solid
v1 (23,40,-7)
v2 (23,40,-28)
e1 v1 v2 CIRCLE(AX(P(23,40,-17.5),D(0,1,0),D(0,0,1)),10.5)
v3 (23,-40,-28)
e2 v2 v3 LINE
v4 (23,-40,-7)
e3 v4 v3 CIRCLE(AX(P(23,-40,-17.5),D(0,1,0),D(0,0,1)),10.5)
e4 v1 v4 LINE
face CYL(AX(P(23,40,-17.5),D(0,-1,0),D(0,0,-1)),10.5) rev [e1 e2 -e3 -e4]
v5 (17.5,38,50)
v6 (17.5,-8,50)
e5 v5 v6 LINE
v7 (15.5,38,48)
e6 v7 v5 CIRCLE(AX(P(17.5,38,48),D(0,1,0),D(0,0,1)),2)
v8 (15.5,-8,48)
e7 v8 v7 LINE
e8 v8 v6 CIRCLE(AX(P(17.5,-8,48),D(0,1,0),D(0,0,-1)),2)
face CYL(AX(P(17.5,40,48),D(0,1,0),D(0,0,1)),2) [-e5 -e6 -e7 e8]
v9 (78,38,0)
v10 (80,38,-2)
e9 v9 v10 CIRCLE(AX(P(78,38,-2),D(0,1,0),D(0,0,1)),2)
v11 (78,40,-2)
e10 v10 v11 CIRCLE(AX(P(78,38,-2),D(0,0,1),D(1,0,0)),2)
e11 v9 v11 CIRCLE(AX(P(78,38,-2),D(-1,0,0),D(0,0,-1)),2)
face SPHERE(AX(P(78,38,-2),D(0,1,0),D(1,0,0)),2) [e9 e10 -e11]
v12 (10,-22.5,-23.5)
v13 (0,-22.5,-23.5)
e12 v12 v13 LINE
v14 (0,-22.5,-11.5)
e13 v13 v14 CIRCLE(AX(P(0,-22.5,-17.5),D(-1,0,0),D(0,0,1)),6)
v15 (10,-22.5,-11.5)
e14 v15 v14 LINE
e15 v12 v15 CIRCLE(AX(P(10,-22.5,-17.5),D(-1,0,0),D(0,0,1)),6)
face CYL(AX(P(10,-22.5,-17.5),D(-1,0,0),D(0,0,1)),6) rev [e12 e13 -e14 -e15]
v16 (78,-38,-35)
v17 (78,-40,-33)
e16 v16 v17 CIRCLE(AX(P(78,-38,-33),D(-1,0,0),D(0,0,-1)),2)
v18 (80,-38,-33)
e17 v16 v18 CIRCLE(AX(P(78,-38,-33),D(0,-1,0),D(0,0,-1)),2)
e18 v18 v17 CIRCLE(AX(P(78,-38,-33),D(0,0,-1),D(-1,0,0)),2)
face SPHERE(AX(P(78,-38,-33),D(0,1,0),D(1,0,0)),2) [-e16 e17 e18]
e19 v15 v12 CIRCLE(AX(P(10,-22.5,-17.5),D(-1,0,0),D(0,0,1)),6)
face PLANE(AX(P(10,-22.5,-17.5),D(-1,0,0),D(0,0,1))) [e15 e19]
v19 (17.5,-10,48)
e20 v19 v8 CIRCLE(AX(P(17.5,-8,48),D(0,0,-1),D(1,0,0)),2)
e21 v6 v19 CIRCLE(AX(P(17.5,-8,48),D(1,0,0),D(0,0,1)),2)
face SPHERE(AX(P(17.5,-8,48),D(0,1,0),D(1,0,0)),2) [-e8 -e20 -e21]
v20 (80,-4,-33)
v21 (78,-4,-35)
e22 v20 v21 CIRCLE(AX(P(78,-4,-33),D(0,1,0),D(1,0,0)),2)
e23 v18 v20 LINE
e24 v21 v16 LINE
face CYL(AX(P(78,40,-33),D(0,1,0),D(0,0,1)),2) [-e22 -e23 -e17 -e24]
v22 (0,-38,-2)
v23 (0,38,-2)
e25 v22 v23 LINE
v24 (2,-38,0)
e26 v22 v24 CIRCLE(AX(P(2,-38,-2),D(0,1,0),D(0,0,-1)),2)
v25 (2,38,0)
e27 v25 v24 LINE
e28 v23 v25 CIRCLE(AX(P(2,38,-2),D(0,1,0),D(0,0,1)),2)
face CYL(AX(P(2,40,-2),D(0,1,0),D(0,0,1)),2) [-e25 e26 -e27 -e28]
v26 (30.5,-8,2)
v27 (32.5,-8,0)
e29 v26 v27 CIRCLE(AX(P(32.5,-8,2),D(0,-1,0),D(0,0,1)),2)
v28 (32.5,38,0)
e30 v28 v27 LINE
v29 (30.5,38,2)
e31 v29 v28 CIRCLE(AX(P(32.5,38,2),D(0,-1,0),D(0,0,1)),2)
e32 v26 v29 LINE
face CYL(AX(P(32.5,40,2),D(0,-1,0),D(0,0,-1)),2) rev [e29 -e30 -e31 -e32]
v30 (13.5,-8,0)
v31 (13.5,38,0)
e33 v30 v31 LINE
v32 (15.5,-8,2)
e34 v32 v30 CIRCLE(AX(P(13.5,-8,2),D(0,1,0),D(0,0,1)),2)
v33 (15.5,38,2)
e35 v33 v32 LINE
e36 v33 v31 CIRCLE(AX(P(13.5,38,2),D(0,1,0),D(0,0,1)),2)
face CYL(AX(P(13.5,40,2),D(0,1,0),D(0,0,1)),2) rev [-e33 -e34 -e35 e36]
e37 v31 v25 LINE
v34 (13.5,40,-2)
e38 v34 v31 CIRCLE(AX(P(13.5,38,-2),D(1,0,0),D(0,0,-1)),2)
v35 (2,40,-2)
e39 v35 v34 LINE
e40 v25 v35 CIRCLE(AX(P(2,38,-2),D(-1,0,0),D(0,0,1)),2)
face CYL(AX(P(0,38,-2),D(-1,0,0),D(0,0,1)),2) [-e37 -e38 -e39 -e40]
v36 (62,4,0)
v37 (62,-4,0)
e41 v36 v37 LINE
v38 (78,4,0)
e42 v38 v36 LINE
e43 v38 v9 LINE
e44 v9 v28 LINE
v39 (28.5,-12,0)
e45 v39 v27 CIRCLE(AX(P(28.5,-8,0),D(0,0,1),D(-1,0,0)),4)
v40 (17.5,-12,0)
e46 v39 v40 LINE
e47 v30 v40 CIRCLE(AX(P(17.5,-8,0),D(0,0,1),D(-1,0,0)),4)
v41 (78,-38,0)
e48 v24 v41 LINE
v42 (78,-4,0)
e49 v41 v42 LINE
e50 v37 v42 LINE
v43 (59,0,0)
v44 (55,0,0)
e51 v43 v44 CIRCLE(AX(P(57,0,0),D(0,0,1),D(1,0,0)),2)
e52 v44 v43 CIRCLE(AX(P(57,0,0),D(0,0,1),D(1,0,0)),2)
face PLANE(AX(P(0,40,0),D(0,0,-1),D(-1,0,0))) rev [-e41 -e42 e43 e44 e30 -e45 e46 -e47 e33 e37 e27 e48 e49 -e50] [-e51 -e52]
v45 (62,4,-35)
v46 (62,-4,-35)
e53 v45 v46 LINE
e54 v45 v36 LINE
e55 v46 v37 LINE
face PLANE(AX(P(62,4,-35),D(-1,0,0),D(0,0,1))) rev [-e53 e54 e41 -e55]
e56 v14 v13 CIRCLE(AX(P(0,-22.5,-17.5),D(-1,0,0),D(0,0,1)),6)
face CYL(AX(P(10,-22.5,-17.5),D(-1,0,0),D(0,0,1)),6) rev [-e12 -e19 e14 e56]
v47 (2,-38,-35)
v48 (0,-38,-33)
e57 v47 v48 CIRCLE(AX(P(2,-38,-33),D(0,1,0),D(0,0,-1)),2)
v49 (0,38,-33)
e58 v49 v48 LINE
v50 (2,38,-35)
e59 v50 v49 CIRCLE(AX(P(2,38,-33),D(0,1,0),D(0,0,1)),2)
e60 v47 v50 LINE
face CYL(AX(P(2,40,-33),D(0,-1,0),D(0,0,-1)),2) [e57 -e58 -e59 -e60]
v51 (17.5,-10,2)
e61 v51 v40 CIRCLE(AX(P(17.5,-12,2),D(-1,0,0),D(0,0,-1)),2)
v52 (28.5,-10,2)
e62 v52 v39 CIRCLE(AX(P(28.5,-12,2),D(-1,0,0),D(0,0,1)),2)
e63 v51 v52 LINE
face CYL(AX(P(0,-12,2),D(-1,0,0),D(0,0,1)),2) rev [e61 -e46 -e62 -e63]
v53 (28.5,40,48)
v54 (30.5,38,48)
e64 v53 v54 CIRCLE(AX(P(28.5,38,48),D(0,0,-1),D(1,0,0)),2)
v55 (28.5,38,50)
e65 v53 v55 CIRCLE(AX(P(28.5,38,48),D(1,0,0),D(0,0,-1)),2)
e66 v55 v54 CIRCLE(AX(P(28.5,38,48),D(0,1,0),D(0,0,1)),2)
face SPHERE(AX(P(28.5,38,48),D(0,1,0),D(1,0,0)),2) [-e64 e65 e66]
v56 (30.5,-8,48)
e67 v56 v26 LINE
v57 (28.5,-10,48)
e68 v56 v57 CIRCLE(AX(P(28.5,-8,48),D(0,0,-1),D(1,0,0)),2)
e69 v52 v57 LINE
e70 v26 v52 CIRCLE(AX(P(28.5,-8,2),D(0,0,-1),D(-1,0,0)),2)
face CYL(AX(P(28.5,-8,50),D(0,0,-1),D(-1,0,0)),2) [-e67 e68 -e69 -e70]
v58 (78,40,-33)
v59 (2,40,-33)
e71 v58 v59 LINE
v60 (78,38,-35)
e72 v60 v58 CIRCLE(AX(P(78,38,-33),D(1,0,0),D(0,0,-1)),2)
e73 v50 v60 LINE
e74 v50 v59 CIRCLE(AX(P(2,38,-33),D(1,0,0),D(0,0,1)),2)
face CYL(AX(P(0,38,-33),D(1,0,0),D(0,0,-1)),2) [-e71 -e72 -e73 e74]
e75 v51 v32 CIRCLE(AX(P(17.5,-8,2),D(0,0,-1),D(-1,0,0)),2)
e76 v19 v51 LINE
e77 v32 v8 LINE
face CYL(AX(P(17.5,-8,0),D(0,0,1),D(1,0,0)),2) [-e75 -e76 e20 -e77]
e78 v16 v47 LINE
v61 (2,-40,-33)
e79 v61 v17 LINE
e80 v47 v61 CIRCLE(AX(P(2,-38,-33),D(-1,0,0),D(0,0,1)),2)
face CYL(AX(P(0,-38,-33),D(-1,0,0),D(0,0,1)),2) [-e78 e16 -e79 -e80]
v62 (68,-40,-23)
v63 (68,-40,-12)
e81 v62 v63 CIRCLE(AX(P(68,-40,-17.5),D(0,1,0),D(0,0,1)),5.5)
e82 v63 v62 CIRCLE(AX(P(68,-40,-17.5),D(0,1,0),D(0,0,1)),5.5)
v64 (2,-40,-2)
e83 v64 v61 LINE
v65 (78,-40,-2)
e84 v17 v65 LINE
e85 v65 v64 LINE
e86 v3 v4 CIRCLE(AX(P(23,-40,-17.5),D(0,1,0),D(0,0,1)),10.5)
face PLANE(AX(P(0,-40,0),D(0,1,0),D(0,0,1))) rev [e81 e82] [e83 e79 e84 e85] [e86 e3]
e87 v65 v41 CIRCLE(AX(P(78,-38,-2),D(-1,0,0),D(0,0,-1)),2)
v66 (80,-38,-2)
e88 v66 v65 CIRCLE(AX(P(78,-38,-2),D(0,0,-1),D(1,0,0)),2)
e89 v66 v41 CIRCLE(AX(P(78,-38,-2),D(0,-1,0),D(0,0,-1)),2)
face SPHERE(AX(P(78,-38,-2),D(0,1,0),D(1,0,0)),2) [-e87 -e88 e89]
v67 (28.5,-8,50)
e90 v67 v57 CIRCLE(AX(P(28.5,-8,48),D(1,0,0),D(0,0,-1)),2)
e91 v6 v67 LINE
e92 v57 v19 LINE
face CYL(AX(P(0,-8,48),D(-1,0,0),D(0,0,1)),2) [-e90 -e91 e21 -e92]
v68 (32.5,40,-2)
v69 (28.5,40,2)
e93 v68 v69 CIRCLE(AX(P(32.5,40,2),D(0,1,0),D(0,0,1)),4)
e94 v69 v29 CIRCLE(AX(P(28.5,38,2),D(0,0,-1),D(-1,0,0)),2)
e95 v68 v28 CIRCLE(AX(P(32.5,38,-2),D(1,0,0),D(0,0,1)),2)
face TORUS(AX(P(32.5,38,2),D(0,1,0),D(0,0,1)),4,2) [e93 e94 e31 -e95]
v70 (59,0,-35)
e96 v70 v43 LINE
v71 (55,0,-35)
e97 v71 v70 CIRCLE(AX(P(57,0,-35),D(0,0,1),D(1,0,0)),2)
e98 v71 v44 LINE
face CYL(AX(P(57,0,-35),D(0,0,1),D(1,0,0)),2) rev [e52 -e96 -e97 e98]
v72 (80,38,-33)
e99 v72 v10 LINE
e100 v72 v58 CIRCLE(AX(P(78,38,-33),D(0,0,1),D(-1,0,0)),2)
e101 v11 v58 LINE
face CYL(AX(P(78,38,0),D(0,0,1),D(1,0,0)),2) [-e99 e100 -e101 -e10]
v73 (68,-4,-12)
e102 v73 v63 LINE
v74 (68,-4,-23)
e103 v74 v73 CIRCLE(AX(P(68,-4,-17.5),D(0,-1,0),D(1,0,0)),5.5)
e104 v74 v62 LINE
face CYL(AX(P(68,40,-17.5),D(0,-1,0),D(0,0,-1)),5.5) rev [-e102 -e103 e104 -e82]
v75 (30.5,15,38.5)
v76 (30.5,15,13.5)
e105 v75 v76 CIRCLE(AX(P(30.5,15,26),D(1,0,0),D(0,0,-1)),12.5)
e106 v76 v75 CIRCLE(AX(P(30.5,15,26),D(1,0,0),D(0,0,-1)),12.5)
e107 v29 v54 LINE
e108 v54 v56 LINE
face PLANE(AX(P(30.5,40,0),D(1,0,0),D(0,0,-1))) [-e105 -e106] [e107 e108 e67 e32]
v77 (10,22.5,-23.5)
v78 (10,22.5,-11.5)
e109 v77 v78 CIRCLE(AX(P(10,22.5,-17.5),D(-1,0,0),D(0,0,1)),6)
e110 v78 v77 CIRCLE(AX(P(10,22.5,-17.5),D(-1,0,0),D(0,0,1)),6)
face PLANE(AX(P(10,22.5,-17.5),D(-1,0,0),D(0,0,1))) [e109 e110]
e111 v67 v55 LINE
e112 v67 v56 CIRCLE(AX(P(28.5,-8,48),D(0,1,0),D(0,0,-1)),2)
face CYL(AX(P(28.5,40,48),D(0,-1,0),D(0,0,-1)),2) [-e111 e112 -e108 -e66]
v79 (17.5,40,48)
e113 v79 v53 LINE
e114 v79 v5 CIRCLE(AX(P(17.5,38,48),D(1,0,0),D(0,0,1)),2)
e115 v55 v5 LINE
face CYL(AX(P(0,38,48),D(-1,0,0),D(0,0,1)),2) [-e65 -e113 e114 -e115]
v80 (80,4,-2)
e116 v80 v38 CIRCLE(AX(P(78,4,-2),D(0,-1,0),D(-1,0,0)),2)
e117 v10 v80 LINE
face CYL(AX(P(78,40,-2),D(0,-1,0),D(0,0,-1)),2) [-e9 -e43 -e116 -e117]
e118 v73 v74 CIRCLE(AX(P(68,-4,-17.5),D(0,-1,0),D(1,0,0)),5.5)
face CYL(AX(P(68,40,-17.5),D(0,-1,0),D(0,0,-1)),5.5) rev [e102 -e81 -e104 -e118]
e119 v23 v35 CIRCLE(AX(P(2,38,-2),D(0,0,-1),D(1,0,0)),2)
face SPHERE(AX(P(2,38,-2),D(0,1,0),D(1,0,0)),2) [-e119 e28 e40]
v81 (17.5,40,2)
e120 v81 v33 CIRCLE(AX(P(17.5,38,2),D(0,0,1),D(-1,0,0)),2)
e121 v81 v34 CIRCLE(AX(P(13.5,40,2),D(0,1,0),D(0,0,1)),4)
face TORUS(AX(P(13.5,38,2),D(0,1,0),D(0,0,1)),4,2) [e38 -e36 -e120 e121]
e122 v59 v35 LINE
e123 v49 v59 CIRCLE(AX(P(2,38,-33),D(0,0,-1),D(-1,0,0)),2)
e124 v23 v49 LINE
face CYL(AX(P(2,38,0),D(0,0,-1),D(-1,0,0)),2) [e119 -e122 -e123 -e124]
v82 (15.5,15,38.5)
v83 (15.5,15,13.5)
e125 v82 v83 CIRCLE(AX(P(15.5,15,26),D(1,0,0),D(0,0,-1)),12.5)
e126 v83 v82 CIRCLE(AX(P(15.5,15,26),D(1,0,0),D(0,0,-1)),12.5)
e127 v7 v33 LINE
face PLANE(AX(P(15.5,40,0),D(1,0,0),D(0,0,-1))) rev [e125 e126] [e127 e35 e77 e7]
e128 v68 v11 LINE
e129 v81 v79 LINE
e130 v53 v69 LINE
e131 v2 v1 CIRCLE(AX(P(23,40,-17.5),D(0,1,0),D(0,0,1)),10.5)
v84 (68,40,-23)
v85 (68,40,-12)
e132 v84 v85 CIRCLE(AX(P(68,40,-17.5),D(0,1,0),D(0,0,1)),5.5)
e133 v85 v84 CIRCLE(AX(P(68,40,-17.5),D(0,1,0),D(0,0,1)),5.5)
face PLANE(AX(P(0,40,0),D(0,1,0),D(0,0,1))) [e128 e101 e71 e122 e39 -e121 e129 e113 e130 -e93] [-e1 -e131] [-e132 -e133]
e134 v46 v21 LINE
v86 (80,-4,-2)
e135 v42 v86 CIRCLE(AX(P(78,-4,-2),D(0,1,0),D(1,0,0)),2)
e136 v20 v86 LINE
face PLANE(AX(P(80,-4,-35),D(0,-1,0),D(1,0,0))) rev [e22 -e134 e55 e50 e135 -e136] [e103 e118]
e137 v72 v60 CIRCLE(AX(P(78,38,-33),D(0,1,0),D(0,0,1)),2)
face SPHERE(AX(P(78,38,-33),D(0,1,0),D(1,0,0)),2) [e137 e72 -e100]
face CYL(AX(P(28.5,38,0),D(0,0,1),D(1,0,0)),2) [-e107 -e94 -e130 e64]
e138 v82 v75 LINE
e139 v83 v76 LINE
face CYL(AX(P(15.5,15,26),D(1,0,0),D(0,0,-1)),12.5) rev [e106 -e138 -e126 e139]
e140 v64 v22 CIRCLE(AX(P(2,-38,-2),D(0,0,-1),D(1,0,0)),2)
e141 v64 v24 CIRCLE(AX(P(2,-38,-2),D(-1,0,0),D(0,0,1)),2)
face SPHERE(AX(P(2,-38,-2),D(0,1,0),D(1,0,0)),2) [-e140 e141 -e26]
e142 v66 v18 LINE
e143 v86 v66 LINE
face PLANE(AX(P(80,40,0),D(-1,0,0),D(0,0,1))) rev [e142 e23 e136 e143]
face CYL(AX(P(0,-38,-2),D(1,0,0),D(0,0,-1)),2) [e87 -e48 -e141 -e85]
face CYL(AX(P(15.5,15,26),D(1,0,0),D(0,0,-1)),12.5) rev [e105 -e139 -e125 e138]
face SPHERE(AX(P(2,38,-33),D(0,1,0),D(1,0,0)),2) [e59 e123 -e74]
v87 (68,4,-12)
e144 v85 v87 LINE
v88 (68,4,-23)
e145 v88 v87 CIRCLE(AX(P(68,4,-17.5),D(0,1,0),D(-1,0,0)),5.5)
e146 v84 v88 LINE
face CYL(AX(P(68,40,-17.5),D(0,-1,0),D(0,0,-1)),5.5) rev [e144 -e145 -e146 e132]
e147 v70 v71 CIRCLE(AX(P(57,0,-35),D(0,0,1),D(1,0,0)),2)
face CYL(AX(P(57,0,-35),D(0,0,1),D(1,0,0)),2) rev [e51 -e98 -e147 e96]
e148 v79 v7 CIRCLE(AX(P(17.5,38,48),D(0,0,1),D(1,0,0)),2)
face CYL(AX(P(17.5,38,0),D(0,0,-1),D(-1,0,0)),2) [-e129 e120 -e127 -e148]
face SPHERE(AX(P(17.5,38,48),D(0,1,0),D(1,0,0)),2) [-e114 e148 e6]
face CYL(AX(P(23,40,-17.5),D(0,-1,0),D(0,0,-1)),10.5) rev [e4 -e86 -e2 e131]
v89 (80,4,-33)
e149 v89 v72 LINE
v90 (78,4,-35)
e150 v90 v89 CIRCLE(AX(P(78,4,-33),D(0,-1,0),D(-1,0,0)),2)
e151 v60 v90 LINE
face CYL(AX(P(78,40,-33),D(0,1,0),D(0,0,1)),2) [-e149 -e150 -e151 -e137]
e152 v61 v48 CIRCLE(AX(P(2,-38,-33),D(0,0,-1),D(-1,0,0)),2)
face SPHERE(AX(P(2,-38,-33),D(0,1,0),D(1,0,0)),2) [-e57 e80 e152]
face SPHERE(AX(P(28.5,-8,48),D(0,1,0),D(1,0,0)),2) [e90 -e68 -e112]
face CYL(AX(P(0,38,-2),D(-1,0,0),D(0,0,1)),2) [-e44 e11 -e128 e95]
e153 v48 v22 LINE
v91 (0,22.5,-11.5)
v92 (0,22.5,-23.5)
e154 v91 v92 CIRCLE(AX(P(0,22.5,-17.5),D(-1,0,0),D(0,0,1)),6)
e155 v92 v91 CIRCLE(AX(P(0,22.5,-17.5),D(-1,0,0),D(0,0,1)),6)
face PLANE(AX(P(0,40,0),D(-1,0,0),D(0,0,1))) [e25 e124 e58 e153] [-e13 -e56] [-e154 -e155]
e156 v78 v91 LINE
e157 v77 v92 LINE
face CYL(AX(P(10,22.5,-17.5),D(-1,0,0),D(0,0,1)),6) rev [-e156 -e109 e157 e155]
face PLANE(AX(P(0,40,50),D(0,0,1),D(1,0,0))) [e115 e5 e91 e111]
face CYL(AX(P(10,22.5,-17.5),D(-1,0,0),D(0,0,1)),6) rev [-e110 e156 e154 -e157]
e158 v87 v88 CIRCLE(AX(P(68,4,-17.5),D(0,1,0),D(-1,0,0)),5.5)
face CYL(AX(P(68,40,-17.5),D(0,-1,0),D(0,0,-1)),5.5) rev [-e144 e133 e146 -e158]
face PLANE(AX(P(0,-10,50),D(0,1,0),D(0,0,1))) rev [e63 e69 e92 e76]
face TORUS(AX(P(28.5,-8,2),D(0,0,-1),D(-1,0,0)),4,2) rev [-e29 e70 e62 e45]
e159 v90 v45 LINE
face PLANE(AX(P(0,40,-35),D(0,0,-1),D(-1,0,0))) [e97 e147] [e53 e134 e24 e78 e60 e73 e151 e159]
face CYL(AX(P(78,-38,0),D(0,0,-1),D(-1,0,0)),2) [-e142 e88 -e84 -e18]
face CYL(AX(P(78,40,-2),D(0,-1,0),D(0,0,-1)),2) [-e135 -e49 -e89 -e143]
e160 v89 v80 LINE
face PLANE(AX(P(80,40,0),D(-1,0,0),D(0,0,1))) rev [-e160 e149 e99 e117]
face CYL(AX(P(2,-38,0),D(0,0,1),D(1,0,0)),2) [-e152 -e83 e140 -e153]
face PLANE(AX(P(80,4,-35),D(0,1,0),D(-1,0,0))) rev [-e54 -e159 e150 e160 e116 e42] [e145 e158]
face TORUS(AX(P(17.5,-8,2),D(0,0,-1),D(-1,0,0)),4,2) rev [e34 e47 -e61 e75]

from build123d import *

# Parameters (mm, degrees)
SKETCH1_W           = 80
SKETCH1_H           = 35
SKETCH1_R           = 5.5
SKETCH1_R_2         = 10.5
SKETCH1_W_2         = 15
SKETCH1_H_2         = 50
BOSS_EXTRUDE1_DEPTH = 40
SKETCH2_R           = 6
CUT_EXTRUDE1_DEPTH  = 10
SKETCH4_W           = 50
SKETCH4_H           = 30
CUT_EXTRUDE3_DEPTH  = 81.933614772
SKETCH3_R           = 12.5
CUT_EXTRUDE2_DEPTH  = 15
SKETCH6_W           = 18
SKETCH6_H           = 8
CUT_EXTRUDE4_DEPTH  = 103.46950766
FILLET1_R           = 2
SKETCH7_R           = 2
CUT_EXTRUDE5_DEPTH  = 103.46950766


with BuildPart() as part:
    # Sketch1 → Boss-Extrude1 (new, symmetric)
    # profile 1 of 2: a face of its own
    with BuildSketch(Plane(origin=(0, 0, 0), x_dir=(1, 0, 0), z_dir=(0, 1, 0))):
        with Locations((40, 17.5)):
            Rectangle(SKETCH1_W, SKETCH1_H)
        with Locations(Location((68, 17.5, 0), (0, 0, 270))):
            Circle(SKETCH1_R, mode=Mode.SUBTRACT)
        with Locations(Location((23, 17.5, 0), (0, 0, 270))):
            Circle(SKETCH1_R_2, mode=Mode.SUBTRACT)
    # profile 2 of 2: a face of its own
    with BuildSketch(Plane(origin=(0, 0, 0), x_dir=(1, 0, 0), z_dir=(0, 1, 0))):
        with Locations((23, -25)):
            Rectangle(SKETCH1_W_2, SKETCH1_H_2)
    extrude(amount=BOSS_EXTRUDE1_DEPTH, both=True)

    # Sketch2 → Cut-Extrude1 (cut)
    with BuildSketch(Plane.ZY):
        with Locations((-17.5, 22.5)):
            Circle(SKETCH2_R)
        with Locations((-17.5, -22.5)):
            Circle(SKETCH2_R)
    extrude(amount=-CUT_EXTRUDE1_DEPTH, mode=Mode.SUBTRACT)

    # Sketch4 → Cut-Extrude3 (cut, through all)
    with BuildSketch(Plane(origin=(30.5, 0, 0), x_dir=(0, 0, -1), z_dir=(1, 0, 0))):
        with Locations((-25, -25)):
            Rectangle(SKETCH4_W, SKETCH4_H)
    extrude(amount=-CUT_EXTRUDE3_DEPTH, mode=Mode.SUBTRACT)

    # Sketch3 → Cut-Extrude2 (cut)
    with BuildSketch(Plane(origin=(30.5, 0, 0), x_dir=(0, 0, -1), z_dir=(1, 0, 0))):
        with Locations((-26, 15)):
            Circle(SKETCH3_R)
    extrude(amount=-CUT_EXTRUDE2_DEPTH, mode=Mode.SUBTRACT)

    # Sketch6 → Cut-Extrude4 (cut, through all)
    with BuildSketch(Plane.XY):
        with Locations((71, 0)):
            Rectangle(SKETCH6_W, SKETCH6_H)
    extrude(amount=-CUT_EXTRUDE4_DEPTH, mode=Mode.SUBTRACT)

    # Fillet1
    fillet1_edges = [part.edges().sort_by_distance(p)[0] for p in [
        (55.25, 40, 0),
        (40, -40, 0),
        (0, -40, -17.5),
        (40, -40, -35),
        (80, 40, -17.5),
        (80, -40, -17.5),
        (40, 40, -35),
        (30.5, 15, 50),
        (15.5, 15, 50),
        (15.5, 15, 0),
        (0, 0, 0),
        (0, 0, -35),
        (80, 22, -35),
        (80, 22, 0),
        (30.5, 15, 0),
        (0, 40, -17.5),
        (7.75, 40, 0),
        (15.5, 40, 25),
        (23, 40, 50),
        (15.5, -10, 25),
        (23, -10, 50),
        (23, -10, 0),
        (30.5, -10, 25),
        (30.5, 40, 25),
        (80, -22, 0),
        (80, -22, -35),
    ]]
    fillet(fillet1_edges, radius=FILLET1_R)

    # Sketch7 → Cut-Extrude5 (cut, through all)
    with BuildSketch(Plane.XY):
        with Locations((57, 0)):
            Circle(SKETCH7_R)
    extrude(amount=-CUT_EXTRUDE5_DEPTH, mode=Mode.SUBTRACT)


solid = part.part
